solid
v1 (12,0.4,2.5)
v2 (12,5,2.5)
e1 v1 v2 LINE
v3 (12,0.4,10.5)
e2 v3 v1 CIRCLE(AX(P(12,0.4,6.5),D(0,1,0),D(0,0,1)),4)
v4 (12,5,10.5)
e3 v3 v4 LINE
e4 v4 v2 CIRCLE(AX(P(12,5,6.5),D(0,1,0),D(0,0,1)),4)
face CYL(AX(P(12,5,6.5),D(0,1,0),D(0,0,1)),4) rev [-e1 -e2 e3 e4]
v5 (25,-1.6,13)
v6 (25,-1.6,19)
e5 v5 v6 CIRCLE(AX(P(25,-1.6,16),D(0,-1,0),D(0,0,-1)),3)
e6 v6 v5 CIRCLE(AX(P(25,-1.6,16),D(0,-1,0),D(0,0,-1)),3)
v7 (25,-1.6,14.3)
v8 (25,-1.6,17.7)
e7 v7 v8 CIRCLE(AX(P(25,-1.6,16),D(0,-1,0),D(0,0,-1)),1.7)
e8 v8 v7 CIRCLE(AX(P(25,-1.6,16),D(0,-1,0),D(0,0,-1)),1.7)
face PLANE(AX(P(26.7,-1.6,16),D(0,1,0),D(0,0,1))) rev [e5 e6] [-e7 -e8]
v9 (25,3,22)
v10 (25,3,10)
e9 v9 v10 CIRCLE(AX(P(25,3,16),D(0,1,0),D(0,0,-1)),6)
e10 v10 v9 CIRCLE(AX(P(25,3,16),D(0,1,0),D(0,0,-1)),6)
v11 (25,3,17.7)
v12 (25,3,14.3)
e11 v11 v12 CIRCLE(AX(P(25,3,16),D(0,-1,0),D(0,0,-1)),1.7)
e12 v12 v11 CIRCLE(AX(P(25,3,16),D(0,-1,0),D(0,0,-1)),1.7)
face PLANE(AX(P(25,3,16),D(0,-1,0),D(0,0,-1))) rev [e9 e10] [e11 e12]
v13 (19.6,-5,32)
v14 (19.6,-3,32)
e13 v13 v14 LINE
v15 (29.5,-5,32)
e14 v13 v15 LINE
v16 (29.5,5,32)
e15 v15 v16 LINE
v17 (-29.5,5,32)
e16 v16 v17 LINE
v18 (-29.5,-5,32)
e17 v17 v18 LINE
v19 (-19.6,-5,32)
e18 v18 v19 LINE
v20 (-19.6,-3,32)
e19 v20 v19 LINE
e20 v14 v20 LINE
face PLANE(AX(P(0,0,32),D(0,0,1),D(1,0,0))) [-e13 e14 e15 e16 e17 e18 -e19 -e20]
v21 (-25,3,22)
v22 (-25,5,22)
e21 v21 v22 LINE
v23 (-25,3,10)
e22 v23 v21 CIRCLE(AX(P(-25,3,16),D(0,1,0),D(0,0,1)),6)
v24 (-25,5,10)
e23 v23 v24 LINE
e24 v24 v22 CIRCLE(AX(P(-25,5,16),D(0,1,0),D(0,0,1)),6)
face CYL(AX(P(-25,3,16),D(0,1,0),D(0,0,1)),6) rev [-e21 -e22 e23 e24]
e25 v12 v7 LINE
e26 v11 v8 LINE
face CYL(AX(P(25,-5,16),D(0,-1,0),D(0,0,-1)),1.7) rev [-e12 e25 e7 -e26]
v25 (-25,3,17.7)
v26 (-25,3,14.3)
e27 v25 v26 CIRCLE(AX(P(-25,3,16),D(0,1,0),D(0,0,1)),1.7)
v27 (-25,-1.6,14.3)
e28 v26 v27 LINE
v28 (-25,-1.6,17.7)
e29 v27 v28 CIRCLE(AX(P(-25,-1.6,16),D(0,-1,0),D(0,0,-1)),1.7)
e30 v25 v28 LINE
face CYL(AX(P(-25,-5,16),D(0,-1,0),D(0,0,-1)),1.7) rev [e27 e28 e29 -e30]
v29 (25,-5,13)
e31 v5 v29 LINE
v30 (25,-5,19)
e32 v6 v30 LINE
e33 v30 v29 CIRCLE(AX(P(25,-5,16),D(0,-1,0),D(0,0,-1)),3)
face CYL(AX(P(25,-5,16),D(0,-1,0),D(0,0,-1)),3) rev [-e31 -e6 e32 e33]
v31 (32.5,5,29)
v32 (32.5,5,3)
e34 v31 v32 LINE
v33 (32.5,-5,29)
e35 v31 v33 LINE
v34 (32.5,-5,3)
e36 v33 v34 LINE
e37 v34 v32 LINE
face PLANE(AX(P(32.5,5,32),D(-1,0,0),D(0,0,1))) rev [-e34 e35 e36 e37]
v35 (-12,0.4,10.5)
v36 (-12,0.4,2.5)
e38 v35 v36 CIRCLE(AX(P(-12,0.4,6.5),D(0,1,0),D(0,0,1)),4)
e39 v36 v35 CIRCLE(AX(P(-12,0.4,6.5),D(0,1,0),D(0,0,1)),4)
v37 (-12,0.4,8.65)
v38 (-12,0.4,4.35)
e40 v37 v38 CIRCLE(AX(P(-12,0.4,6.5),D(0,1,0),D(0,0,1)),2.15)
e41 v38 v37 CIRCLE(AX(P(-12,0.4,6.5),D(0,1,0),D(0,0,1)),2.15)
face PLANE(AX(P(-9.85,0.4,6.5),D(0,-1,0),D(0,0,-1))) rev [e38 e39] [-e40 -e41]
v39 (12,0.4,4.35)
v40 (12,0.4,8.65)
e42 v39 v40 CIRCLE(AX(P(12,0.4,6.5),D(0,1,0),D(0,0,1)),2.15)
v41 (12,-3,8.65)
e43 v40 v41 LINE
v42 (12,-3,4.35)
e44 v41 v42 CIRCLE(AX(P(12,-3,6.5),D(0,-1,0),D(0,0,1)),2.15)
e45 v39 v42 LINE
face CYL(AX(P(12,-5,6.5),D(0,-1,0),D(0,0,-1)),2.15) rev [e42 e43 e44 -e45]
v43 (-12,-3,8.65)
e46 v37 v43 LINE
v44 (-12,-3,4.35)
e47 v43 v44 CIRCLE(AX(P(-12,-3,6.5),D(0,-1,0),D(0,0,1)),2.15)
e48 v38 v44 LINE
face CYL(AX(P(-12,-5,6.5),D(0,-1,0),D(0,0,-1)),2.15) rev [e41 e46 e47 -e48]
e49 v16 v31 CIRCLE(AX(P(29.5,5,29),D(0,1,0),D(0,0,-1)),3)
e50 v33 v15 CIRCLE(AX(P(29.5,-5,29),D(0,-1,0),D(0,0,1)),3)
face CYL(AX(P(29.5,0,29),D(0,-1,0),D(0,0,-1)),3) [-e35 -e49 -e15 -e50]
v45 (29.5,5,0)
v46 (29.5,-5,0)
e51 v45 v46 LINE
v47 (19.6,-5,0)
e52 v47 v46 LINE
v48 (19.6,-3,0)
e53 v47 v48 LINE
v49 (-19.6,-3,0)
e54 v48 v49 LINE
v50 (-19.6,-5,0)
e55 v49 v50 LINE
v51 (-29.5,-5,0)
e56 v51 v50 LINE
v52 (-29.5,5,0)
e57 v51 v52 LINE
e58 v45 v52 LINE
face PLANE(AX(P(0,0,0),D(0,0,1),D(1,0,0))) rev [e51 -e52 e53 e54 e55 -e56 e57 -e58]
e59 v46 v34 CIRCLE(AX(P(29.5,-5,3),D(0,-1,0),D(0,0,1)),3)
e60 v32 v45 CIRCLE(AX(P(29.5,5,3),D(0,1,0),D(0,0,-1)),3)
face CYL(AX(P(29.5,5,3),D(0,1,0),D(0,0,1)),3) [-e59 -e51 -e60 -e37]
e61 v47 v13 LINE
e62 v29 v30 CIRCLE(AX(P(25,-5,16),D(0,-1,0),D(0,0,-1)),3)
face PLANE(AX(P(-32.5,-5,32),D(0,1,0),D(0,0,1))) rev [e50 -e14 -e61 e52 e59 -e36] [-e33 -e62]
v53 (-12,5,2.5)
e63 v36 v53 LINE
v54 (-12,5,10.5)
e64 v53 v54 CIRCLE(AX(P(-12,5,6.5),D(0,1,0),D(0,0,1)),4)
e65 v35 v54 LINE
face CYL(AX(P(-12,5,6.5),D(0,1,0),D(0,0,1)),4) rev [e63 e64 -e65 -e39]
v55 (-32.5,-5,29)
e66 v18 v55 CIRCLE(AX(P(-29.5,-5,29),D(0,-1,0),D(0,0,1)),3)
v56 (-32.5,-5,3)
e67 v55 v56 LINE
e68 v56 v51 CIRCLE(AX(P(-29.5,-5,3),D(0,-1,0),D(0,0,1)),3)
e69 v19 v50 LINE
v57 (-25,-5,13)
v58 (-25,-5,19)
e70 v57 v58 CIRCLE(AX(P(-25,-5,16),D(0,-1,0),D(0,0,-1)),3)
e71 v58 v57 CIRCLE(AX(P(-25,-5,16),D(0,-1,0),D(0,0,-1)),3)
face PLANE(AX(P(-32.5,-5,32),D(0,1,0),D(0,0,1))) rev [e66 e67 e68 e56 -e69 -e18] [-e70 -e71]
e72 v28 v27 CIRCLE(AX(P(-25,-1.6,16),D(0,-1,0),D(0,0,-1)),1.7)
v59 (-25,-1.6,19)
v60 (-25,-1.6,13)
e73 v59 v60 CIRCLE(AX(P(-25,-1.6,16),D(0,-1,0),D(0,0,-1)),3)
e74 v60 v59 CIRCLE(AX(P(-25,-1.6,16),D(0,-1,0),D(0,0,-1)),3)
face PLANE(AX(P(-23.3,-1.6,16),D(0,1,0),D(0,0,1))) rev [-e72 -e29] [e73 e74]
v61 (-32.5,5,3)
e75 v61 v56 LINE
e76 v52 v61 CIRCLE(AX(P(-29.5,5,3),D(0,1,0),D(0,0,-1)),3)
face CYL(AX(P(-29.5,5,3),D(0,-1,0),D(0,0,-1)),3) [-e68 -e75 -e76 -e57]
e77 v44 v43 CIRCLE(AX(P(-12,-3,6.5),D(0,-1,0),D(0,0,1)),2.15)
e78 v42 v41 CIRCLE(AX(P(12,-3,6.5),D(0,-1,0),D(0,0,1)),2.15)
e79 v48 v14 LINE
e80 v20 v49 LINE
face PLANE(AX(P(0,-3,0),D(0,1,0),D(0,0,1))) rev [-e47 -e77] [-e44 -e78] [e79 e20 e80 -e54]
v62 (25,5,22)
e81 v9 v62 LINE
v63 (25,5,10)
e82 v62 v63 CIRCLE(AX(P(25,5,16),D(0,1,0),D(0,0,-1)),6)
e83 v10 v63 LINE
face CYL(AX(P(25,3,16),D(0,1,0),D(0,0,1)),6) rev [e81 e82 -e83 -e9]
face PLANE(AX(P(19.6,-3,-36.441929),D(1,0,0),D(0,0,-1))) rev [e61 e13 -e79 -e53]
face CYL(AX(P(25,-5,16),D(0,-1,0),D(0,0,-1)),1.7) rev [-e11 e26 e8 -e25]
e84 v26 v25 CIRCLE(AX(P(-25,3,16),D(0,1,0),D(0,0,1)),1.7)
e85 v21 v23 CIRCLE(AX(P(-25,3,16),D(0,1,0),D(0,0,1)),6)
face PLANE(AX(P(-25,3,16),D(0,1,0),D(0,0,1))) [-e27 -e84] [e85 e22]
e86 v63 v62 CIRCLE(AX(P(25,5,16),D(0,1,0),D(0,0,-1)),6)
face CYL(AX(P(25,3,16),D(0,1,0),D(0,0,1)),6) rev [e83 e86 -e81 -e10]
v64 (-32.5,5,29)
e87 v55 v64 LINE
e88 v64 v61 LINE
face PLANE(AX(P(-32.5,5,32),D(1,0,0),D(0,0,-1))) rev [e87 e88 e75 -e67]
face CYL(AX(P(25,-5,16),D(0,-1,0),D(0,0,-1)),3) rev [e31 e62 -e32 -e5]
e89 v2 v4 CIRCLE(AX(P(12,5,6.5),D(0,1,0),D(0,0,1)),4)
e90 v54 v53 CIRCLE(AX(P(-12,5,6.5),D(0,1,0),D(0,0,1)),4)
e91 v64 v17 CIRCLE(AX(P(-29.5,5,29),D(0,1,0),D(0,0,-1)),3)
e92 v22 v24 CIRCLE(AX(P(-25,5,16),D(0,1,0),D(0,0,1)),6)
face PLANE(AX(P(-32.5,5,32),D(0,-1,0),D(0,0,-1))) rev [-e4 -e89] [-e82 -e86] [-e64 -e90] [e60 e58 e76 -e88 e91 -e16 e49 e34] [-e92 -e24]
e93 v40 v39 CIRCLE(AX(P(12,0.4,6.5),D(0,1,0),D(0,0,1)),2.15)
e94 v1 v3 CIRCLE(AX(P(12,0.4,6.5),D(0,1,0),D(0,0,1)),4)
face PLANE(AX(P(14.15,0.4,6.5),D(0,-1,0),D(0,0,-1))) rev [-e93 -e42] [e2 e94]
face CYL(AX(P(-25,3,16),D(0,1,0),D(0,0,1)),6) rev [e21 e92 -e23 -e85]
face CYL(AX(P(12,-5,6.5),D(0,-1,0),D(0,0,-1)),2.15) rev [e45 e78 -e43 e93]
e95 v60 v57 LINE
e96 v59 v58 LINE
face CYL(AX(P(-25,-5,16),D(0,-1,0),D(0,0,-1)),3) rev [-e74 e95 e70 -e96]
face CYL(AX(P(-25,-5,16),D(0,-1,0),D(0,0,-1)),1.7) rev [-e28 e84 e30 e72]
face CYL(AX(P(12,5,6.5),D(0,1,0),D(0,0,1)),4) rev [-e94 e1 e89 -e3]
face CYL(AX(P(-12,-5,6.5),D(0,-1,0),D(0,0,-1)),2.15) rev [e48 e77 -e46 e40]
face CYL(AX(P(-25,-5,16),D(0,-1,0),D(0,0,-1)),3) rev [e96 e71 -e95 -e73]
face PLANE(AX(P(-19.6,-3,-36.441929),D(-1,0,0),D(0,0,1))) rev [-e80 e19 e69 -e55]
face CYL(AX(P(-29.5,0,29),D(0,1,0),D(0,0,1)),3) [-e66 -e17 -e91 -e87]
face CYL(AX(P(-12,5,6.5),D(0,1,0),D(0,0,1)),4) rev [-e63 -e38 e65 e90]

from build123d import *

# Parameters (mm, degrees)
SKETCH_1_W                = 65
SKETCH_1_H                = 10
EXTRUDE_1_DEPTH           = 32
HOLE_WIZARD_5_0_5_1_D     = 4.3
FILLET_1_R                = 3
SKETCH_10_R               = 6
CUT_EXTRUDE_3_DEPTH       = 2
HOLE_WIZARD_1_D           = 3.4
HOLE_WIZARD_1_CBORE_D     = 6
HOLE_WIZARD_1_CBORE_DEPTH = 3.4
HOLE_WIZARD_2_D           = 4.3
HOLE_WIZARD_2_CBORE_D     = 8
HOLE_WIZARD_2_CBORE_DEPTH = 4.6
SKETCH_16_W               = 39.2
SKETCH_16_H               = 72.88385863
CUT_EXTRUDE_4_DEPTH       = 2


with BuildPart() as part:
    # 草图1 → 凸台-拉伸1 (new body)
    with BuildSketch(Plane.XY):
        Rectangle(SKETCH_1_W, SKETCH_1_H)
    extrude(amount=EXTRUDE_1_DEPTH)

    # Ø5.0 (5) 直径孔1 (through all)
    with Locations(Plane.XZ.offset(5)):
        with Locations((-12, 6.5), (12, 6.5)):
            Hole(HOLE_WIZARD_5_0_5_1_D / 2)

    # 圆角1
    fillet_1_edges = [part.edges().sort_by_distance(p)[0] for p in [
        (-32.5, 0, 32),
        (32.5, 0, 32),
        (-32.5, 0, 0),
        (32.5, 0, 0),
    ]]
    fillet(fillet_1_edges, radius=FILLET_1_R)

    # 草图10 → 切除-拉伸3 (cut)
    with BuildSketch(Plane(origin=(0, 5, 0), x_dir=(1, 0, 0), z_dir=(0, 1, 0))):
        with Locations(Location((-25, -16, 0), (0, 0, 270))):
            Circle(SKETCH_10_R)
        with Locations(Location((25, -16, 0), (0, 0, 90))):
            Circle(SKETCH_10_R)
    extrude(amount=-CUT_EXTRUDE_3_DEPTH, mode=Mode.SUBTRACT)

    # 打孔尺寸(%根据)开槽圆柱头螺钉的类型1 (through all)
    with Locations(Plane(origin=(0, -5, 0), x_dir=(-1, 0, 0), z_dir=(0, -1, 0))):
        with Locations((-25, -16), (25, -16)):
            CounterBoreHole(HOLE_WIZARD_1_D / 2, HOLE_WIZARD_1_CBORE_D / 2, HOLE_WIZARD_1_CBORE_DEPTH)

    # 打孔尺寸(%根据)开槽圆柱头螺钉的类型2 (through all)
    with Locations(Plane(origin=(0, 5, 0), x_dir=(1, 0, 0), z_dir=(0, 1, 0))):
        with Locations((-12, -6.5), (12, -6.5)):
            CounterBoreHole(HOLE_WIZARD_2_D / 2, HOLE_WIZARD_2_CBORE_D / 2, HOLE_WIZARD_2_CBORE_DEPTH)

    # 草图16 → 切除-拉伸4 (cut)
    with BuildSketch(Plane.XZ.offset(5)):
        Rectangle(SKETCH_16_W, SKETCH_16_H)
    extrude(amount=-CUT_EXTRUDE_4_DEPTH, mode=Mode.SUBTRACT)


solid = part.part
